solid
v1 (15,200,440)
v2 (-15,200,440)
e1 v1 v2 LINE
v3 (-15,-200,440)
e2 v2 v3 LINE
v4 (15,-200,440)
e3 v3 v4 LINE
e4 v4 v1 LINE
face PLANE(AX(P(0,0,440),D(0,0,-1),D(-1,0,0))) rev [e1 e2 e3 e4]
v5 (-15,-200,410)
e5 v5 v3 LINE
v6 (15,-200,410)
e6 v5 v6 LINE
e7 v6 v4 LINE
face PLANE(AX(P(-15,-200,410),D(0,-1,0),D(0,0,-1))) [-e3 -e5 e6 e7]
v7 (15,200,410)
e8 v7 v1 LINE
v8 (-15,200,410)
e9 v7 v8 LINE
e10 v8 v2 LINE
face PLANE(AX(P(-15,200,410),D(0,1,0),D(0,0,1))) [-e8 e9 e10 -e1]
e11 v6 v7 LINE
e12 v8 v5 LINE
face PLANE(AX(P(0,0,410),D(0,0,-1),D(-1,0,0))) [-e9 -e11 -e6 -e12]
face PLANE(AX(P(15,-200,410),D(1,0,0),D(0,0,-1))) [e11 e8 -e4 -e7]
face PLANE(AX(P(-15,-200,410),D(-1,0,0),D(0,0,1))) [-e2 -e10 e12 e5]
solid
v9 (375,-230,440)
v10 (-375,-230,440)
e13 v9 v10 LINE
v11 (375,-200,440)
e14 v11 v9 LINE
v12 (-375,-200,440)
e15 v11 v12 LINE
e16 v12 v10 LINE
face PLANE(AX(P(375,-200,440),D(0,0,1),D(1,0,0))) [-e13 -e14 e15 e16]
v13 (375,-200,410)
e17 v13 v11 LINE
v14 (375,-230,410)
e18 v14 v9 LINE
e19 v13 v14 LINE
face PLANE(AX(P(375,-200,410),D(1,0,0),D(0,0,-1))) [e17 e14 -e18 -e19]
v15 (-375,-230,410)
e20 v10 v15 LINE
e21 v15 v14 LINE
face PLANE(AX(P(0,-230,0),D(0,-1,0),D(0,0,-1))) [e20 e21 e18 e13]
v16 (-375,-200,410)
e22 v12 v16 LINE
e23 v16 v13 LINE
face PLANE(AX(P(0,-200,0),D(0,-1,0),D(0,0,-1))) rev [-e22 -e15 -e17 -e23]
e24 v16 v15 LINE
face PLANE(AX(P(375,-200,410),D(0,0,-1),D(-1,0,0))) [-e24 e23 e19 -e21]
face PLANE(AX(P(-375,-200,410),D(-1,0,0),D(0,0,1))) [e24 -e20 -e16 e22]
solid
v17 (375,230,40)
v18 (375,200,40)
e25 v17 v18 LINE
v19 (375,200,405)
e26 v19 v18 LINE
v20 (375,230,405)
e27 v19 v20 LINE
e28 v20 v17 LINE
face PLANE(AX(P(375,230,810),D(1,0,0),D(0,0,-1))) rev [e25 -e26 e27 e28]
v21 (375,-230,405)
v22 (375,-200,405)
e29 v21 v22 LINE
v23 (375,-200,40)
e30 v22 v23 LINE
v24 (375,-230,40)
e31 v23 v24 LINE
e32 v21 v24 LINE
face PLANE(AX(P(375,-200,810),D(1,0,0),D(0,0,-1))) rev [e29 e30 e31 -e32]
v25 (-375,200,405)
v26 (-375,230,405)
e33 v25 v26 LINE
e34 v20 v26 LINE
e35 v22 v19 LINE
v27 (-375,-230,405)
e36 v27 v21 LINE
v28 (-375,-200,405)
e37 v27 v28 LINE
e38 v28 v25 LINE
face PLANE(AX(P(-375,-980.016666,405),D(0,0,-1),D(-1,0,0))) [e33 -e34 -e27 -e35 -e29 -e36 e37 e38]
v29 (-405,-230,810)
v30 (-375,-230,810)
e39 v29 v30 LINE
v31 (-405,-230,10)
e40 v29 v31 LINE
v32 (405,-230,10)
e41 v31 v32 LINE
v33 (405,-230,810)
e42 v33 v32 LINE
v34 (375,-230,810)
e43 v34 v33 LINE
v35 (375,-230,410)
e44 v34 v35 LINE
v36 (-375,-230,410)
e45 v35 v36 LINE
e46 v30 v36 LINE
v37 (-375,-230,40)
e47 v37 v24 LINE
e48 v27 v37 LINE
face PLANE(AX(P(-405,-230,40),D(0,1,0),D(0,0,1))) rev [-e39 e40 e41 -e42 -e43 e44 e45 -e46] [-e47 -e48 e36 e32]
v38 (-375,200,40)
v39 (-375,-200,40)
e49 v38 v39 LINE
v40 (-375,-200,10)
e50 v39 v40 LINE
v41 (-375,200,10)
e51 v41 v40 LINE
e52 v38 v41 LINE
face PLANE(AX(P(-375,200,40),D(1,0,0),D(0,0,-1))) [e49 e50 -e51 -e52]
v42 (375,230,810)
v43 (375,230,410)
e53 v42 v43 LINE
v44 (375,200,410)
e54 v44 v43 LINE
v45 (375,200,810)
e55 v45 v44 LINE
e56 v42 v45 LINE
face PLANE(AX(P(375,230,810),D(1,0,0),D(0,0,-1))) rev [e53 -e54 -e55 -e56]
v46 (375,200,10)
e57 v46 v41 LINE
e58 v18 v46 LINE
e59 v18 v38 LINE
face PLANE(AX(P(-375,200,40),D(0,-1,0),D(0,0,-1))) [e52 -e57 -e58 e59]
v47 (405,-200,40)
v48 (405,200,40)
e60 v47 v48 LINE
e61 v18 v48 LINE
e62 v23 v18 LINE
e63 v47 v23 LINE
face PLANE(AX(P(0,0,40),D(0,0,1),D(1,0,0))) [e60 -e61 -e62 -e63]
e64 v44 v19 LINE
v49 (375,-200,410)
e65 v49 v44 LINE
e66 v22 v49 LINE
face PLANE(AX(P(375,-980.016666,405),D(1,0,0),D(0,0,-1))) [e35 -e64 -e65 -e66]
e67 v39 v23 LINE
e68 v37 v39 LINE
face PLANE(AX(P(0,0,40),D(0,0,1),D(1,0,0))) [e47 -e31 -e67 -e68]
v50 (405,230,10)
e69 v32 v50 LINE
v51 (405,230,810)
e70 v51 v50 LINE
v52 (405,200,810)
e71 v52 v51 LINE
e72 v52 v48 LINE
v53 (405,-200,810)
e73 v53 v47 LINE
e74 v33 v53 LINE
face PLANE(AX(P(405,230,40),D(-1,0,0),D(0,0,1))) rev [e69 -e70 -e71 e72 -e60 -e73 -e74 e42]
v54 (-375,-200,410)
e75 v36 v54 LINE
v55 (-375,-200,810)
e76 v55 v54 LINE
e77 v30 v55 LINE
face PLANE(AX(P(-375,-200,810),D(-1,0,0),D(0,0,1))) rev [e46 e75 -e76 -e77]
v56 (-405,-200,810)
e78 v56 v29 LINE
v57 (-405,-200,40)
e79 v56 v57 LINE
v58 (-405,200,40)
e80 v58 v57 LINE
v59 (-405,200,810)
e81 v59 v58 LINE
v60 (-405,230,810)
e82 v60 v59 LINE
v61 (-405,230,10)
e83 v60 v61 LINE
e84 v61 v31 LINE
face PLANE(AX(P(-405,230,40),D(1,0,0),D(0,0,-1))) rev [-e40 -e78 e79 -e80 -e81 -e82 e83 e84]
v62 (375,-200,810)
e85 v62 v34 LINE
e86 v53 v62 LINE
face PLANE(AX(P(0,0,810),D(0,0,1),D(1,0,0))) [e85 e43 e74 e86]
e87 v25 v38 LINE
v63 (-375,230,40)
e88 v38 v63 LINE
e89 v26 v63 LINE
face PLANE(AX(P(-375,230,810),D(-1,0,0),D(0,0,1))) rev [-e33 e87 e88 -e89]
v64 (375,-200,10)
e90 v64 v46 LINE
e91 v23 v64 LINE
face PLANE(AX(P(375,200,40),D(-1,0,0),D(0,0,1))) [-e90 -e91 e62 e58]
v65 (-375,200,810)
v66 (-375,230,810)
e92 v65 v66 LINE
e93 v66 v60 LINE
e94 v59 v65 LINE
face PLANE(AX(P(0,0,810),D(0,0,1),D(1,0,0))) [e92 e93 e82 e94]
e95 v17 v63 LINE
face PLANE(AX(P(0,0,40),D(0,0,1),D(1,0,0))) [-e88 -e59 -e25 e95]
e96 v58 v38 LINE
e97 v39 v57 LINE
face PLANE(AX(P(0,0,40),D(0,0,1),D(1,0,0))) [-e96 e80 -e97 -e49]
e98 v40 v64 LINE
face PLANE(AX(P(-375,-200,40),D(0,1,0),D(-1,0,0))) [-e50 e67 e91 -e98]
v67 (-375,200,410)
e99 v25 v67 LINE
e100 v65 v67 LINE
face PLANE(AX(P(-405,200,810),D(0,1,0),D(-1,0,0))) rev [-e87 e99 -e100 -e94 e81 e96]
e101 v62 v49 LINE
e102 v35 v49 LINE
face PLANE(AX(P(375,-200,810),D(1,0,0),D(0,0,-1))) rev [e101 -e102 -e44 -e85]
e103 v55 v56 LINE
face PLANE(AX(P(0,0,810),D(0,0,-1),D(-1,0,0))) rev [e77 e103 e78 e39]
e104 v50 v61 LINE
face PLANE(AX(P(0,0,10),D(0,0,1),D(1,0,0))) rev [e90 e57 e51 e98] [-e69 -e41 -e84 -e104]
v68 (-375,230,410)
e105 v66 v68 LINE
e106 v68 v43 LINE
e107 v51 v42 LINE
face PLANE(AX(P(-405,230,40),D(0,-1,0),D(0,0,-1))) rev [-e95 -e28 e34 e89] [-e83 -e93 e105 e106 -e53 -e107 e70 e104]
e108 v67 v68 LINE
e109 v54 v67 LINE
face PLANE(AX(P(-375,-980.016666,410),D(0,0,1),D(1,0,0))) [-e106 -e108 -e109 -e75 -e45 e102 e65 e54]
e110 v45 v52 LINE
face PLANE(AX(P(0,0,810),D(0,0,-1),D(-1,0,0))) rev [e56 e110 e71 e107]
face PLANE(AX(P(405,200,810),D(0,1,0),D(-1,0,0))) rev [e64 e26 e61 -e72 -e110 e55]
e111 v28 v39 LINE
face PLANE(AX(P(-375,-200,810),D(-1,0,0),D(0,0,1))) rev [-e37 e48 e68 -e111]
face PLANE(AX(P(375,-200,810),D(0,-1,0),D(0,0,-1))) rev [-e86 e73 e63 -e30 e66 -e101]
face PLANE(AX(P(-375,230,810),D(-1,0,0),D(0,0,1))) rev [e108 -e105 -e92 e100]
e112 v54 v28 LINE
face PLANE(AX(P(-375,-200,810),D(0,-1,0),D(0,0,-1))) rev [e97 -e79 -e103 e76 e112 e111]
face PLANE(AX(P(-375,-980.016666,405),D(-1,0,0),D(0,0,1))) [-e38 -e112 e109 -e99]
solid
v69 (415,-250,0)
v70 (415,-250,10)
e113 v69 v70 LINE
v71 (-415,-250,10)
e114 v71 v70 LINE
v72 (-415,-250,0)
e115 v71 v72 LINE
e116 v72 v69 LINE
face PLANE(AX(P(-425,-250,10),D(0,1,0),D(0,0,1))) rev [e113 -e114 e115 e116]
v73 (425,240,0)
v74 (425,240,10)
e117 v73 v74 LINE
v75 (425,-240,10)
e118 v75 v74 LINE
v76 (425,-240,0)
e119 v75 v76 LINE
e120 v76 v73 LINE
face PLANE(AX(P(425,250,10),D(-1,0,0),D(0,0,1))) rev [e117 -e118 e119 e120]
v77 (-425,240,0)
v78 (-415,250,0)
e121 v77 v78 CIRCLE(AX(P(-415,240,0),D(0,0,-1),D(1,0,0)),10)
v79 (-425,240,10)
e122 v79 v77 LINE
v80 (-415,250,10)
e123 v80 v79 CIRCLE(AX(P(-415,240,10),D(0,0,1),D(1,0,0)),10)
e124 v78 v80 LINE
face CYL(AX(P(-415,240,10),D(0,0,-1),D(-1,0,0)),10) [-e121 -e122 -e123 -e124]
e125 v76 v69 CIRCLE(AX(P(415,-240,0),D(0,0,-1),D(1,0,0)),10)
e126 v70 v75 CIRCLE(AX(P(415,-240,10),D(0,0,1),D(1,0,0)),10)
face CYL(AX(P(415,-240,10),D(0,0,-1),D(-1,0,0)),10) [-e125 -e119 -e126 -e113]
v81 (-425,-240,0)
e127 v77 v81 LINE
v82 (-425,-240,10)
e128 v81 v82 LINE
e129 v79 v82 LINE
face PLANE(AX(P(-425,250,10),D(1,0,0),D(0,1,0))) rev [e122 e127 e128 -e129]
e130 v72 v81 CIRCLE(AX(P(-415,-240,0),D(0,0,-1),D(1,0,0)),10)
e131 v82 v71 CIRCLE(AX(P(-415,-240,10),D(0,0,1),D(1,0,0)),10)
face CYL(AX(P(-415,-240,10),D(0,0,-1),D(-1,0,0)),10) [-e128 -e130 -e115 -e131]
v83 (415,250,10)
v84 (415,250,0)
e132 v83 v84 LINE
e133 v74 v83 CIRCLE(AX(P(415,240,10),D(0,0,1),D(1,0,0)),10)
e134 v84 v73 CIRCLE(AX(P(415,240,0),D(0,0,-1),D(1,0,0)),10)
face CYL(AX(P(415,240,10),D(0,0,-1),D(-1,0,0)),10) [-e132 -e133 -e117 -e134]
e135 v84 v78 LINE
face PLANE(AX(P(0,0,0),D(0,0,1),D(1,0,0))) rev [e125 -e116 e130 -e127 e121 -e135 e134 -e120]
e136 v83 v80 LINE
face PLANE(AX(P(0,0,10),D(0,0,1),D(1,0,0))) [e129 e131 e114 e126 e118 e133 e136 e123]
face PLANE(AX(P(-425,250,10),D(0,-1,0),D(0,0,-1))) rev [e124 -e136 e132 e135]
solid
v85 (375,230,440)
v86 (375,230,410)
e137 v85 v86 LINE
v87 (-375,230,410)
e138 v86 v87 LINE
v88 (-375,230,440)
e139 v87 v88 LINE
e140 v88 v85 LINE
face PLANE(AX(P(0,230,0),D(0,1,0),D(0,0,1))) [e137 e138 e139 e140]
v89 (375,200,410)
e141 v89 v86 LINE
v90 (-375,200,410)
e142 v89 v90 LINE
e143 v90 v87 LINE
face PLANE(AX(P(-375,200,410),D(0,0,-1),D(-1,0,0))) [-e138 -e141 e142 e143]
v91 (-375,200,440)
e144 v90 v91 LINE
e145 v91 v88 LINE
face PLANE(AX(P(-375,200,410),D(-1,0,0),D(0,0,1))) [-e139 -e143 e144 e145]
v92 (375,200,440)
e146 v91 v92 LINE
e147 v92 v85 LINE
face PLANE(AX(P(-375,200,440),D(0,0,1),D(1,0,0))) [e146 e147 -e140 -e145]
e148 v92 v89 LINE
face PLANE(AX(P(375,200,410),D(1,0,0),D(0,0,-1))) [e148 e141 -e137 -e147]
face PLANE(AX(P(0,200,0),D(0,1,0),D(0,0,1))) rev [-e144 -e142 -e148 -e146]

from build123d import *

# Parameters (mm, degrees)
SKETCH_1_W      = 850
SKETCH_1_H      = 500
EXTRUDE_1_DEPTH = 10
SKETCH_2_W      = 810
SKETCH_2_H      = 460
SKETCH_2_W_2    = 750
SKETCH_2_H_2    = 400
EXTRUDE_2_DEPTH = 30
SKETCH_3_W      = 30
SKETCH_3_H      = 30
EXTRUDE_3_DEPTH = 770
EXTRUDE_START   = -460
SKETCH_4_W      = 750
SKETCH_4_H      = 5
EXTRUDE_4_DEPTH = 460
SKETCH_6_W      = 750
SKETCH_6_H      = 30
EXTRUDE_7_DEPTH = 30
SKETCH_7_W      = 750
SKETCH_7_H      = 30
EXTRUDE_8_DEPTH = 30
SKETCH_8_W      = 30
SKETCH_8_H      = 400
EXTRUDE_9_DEPTH = 30
FILLET_1_R      = 10


with BuildPart() as part:
    # 草图1 → 凸台-拉伸1 (new body)
    with BuildSketch(Plane.XY):
        Rectangle(SKETCH_1_W, SKETCH_1_H)
    extrude(amount=EXTRUDE_1_DEPTH)

    # 圆角1
    fillet_1_edges = [part.edges().sort_by_distance(p)[0] for p in [
        (425, -250, 5),
        (-425, -250, 5),
        (-425, 250, 5),
        (425, 250, 5),
    ]]
    fillet(fillet_1_edges, radius=FILLET_1_R)


with BuildPart() as body_2:
    # 草图2 → 凸台-拉伸2 (new body)
    with BuildSketch(Plane.XY.offset(10)):
        Rectangle(SKETCH_2_W, SKETCH_2_H)
        Rectangle(SKETCH_2_W_2, SKETCH_2_H_2, mode=Mode.SUBTRACT)
    extrude(amount=EXTRUDE_2_DEPTH)

    # 草图3 → 凸台-拉伸3 (add)
    with BuildSketch(Plane.XY.offset(40)):
        with Locations((-390, 215)):
            Rectangle(SKETCH_3_W, SKETCH_3_H)
        with Locations((390, -215)):
            Rectangle(SKETCH_3_W, SKETCH_3_H)
        with Locations((390, 215)):
            Rectangle(SKETCH_3_W, SKETCH_3_H)
        with Locations((-390, -215)):
            Rectangle(SKETCH_3_W, SKETCH_3_H)
    extrude(amount=EXTRUDE_3_DEPTH)

    # 草图4 → 凸台-拉伸4 (add)
    with BuildSketch(Plane(origin=(0, 230, 0), x_dir=(1, 0, 0), z_dir=(0, 1, 0)).offset(EXTRUDE_START)):
        with Locations((0, -407.5)):
            Rectangle(SKETCH_4_W, SKETCH_4_H)
    extrude(amount=EXTRUDE_4_DEPTH)


with BuildPart() as body_3:
    # 草图6 → 凸台-拉伸7 (new body)
    with BuildSketch(Plane.XZ.offset(230)):
        with Locations((0, 425)):
            Rectangle(SKETCH_6_W, SKETCH_6_H)
    extrude(amount=-EXTRUDE_7_DEPTH)


with BuildPart() as body_4:
    # 草图7 → 凸台-拉伸8 (new body)
    with BuildSketch(Plane(origin=(0, 230, 0), x_dir=(1, 0, 0), z_dir=(0, 1, 0))):
        with Locations((0, -425)):
            Rectangle(SKETCH_7_W, SKETCH_7_H)
    extrude(amount=-EXTRUDE_8_DEPTH)


with BuildPart() as body_5:
    # 草图8 → 凸台-拉伸9 (new body)
    with BuildSketch(Plane.XY.offset(440)):
        Rectangle(SKETCH_8_W, SKETCH_8_H)
    extrude(amount=-EXTRUDE_9_DEPTH)


solid = Compound([part.part, body_2.part, body_3.part, body_4.part, body_5.part])
